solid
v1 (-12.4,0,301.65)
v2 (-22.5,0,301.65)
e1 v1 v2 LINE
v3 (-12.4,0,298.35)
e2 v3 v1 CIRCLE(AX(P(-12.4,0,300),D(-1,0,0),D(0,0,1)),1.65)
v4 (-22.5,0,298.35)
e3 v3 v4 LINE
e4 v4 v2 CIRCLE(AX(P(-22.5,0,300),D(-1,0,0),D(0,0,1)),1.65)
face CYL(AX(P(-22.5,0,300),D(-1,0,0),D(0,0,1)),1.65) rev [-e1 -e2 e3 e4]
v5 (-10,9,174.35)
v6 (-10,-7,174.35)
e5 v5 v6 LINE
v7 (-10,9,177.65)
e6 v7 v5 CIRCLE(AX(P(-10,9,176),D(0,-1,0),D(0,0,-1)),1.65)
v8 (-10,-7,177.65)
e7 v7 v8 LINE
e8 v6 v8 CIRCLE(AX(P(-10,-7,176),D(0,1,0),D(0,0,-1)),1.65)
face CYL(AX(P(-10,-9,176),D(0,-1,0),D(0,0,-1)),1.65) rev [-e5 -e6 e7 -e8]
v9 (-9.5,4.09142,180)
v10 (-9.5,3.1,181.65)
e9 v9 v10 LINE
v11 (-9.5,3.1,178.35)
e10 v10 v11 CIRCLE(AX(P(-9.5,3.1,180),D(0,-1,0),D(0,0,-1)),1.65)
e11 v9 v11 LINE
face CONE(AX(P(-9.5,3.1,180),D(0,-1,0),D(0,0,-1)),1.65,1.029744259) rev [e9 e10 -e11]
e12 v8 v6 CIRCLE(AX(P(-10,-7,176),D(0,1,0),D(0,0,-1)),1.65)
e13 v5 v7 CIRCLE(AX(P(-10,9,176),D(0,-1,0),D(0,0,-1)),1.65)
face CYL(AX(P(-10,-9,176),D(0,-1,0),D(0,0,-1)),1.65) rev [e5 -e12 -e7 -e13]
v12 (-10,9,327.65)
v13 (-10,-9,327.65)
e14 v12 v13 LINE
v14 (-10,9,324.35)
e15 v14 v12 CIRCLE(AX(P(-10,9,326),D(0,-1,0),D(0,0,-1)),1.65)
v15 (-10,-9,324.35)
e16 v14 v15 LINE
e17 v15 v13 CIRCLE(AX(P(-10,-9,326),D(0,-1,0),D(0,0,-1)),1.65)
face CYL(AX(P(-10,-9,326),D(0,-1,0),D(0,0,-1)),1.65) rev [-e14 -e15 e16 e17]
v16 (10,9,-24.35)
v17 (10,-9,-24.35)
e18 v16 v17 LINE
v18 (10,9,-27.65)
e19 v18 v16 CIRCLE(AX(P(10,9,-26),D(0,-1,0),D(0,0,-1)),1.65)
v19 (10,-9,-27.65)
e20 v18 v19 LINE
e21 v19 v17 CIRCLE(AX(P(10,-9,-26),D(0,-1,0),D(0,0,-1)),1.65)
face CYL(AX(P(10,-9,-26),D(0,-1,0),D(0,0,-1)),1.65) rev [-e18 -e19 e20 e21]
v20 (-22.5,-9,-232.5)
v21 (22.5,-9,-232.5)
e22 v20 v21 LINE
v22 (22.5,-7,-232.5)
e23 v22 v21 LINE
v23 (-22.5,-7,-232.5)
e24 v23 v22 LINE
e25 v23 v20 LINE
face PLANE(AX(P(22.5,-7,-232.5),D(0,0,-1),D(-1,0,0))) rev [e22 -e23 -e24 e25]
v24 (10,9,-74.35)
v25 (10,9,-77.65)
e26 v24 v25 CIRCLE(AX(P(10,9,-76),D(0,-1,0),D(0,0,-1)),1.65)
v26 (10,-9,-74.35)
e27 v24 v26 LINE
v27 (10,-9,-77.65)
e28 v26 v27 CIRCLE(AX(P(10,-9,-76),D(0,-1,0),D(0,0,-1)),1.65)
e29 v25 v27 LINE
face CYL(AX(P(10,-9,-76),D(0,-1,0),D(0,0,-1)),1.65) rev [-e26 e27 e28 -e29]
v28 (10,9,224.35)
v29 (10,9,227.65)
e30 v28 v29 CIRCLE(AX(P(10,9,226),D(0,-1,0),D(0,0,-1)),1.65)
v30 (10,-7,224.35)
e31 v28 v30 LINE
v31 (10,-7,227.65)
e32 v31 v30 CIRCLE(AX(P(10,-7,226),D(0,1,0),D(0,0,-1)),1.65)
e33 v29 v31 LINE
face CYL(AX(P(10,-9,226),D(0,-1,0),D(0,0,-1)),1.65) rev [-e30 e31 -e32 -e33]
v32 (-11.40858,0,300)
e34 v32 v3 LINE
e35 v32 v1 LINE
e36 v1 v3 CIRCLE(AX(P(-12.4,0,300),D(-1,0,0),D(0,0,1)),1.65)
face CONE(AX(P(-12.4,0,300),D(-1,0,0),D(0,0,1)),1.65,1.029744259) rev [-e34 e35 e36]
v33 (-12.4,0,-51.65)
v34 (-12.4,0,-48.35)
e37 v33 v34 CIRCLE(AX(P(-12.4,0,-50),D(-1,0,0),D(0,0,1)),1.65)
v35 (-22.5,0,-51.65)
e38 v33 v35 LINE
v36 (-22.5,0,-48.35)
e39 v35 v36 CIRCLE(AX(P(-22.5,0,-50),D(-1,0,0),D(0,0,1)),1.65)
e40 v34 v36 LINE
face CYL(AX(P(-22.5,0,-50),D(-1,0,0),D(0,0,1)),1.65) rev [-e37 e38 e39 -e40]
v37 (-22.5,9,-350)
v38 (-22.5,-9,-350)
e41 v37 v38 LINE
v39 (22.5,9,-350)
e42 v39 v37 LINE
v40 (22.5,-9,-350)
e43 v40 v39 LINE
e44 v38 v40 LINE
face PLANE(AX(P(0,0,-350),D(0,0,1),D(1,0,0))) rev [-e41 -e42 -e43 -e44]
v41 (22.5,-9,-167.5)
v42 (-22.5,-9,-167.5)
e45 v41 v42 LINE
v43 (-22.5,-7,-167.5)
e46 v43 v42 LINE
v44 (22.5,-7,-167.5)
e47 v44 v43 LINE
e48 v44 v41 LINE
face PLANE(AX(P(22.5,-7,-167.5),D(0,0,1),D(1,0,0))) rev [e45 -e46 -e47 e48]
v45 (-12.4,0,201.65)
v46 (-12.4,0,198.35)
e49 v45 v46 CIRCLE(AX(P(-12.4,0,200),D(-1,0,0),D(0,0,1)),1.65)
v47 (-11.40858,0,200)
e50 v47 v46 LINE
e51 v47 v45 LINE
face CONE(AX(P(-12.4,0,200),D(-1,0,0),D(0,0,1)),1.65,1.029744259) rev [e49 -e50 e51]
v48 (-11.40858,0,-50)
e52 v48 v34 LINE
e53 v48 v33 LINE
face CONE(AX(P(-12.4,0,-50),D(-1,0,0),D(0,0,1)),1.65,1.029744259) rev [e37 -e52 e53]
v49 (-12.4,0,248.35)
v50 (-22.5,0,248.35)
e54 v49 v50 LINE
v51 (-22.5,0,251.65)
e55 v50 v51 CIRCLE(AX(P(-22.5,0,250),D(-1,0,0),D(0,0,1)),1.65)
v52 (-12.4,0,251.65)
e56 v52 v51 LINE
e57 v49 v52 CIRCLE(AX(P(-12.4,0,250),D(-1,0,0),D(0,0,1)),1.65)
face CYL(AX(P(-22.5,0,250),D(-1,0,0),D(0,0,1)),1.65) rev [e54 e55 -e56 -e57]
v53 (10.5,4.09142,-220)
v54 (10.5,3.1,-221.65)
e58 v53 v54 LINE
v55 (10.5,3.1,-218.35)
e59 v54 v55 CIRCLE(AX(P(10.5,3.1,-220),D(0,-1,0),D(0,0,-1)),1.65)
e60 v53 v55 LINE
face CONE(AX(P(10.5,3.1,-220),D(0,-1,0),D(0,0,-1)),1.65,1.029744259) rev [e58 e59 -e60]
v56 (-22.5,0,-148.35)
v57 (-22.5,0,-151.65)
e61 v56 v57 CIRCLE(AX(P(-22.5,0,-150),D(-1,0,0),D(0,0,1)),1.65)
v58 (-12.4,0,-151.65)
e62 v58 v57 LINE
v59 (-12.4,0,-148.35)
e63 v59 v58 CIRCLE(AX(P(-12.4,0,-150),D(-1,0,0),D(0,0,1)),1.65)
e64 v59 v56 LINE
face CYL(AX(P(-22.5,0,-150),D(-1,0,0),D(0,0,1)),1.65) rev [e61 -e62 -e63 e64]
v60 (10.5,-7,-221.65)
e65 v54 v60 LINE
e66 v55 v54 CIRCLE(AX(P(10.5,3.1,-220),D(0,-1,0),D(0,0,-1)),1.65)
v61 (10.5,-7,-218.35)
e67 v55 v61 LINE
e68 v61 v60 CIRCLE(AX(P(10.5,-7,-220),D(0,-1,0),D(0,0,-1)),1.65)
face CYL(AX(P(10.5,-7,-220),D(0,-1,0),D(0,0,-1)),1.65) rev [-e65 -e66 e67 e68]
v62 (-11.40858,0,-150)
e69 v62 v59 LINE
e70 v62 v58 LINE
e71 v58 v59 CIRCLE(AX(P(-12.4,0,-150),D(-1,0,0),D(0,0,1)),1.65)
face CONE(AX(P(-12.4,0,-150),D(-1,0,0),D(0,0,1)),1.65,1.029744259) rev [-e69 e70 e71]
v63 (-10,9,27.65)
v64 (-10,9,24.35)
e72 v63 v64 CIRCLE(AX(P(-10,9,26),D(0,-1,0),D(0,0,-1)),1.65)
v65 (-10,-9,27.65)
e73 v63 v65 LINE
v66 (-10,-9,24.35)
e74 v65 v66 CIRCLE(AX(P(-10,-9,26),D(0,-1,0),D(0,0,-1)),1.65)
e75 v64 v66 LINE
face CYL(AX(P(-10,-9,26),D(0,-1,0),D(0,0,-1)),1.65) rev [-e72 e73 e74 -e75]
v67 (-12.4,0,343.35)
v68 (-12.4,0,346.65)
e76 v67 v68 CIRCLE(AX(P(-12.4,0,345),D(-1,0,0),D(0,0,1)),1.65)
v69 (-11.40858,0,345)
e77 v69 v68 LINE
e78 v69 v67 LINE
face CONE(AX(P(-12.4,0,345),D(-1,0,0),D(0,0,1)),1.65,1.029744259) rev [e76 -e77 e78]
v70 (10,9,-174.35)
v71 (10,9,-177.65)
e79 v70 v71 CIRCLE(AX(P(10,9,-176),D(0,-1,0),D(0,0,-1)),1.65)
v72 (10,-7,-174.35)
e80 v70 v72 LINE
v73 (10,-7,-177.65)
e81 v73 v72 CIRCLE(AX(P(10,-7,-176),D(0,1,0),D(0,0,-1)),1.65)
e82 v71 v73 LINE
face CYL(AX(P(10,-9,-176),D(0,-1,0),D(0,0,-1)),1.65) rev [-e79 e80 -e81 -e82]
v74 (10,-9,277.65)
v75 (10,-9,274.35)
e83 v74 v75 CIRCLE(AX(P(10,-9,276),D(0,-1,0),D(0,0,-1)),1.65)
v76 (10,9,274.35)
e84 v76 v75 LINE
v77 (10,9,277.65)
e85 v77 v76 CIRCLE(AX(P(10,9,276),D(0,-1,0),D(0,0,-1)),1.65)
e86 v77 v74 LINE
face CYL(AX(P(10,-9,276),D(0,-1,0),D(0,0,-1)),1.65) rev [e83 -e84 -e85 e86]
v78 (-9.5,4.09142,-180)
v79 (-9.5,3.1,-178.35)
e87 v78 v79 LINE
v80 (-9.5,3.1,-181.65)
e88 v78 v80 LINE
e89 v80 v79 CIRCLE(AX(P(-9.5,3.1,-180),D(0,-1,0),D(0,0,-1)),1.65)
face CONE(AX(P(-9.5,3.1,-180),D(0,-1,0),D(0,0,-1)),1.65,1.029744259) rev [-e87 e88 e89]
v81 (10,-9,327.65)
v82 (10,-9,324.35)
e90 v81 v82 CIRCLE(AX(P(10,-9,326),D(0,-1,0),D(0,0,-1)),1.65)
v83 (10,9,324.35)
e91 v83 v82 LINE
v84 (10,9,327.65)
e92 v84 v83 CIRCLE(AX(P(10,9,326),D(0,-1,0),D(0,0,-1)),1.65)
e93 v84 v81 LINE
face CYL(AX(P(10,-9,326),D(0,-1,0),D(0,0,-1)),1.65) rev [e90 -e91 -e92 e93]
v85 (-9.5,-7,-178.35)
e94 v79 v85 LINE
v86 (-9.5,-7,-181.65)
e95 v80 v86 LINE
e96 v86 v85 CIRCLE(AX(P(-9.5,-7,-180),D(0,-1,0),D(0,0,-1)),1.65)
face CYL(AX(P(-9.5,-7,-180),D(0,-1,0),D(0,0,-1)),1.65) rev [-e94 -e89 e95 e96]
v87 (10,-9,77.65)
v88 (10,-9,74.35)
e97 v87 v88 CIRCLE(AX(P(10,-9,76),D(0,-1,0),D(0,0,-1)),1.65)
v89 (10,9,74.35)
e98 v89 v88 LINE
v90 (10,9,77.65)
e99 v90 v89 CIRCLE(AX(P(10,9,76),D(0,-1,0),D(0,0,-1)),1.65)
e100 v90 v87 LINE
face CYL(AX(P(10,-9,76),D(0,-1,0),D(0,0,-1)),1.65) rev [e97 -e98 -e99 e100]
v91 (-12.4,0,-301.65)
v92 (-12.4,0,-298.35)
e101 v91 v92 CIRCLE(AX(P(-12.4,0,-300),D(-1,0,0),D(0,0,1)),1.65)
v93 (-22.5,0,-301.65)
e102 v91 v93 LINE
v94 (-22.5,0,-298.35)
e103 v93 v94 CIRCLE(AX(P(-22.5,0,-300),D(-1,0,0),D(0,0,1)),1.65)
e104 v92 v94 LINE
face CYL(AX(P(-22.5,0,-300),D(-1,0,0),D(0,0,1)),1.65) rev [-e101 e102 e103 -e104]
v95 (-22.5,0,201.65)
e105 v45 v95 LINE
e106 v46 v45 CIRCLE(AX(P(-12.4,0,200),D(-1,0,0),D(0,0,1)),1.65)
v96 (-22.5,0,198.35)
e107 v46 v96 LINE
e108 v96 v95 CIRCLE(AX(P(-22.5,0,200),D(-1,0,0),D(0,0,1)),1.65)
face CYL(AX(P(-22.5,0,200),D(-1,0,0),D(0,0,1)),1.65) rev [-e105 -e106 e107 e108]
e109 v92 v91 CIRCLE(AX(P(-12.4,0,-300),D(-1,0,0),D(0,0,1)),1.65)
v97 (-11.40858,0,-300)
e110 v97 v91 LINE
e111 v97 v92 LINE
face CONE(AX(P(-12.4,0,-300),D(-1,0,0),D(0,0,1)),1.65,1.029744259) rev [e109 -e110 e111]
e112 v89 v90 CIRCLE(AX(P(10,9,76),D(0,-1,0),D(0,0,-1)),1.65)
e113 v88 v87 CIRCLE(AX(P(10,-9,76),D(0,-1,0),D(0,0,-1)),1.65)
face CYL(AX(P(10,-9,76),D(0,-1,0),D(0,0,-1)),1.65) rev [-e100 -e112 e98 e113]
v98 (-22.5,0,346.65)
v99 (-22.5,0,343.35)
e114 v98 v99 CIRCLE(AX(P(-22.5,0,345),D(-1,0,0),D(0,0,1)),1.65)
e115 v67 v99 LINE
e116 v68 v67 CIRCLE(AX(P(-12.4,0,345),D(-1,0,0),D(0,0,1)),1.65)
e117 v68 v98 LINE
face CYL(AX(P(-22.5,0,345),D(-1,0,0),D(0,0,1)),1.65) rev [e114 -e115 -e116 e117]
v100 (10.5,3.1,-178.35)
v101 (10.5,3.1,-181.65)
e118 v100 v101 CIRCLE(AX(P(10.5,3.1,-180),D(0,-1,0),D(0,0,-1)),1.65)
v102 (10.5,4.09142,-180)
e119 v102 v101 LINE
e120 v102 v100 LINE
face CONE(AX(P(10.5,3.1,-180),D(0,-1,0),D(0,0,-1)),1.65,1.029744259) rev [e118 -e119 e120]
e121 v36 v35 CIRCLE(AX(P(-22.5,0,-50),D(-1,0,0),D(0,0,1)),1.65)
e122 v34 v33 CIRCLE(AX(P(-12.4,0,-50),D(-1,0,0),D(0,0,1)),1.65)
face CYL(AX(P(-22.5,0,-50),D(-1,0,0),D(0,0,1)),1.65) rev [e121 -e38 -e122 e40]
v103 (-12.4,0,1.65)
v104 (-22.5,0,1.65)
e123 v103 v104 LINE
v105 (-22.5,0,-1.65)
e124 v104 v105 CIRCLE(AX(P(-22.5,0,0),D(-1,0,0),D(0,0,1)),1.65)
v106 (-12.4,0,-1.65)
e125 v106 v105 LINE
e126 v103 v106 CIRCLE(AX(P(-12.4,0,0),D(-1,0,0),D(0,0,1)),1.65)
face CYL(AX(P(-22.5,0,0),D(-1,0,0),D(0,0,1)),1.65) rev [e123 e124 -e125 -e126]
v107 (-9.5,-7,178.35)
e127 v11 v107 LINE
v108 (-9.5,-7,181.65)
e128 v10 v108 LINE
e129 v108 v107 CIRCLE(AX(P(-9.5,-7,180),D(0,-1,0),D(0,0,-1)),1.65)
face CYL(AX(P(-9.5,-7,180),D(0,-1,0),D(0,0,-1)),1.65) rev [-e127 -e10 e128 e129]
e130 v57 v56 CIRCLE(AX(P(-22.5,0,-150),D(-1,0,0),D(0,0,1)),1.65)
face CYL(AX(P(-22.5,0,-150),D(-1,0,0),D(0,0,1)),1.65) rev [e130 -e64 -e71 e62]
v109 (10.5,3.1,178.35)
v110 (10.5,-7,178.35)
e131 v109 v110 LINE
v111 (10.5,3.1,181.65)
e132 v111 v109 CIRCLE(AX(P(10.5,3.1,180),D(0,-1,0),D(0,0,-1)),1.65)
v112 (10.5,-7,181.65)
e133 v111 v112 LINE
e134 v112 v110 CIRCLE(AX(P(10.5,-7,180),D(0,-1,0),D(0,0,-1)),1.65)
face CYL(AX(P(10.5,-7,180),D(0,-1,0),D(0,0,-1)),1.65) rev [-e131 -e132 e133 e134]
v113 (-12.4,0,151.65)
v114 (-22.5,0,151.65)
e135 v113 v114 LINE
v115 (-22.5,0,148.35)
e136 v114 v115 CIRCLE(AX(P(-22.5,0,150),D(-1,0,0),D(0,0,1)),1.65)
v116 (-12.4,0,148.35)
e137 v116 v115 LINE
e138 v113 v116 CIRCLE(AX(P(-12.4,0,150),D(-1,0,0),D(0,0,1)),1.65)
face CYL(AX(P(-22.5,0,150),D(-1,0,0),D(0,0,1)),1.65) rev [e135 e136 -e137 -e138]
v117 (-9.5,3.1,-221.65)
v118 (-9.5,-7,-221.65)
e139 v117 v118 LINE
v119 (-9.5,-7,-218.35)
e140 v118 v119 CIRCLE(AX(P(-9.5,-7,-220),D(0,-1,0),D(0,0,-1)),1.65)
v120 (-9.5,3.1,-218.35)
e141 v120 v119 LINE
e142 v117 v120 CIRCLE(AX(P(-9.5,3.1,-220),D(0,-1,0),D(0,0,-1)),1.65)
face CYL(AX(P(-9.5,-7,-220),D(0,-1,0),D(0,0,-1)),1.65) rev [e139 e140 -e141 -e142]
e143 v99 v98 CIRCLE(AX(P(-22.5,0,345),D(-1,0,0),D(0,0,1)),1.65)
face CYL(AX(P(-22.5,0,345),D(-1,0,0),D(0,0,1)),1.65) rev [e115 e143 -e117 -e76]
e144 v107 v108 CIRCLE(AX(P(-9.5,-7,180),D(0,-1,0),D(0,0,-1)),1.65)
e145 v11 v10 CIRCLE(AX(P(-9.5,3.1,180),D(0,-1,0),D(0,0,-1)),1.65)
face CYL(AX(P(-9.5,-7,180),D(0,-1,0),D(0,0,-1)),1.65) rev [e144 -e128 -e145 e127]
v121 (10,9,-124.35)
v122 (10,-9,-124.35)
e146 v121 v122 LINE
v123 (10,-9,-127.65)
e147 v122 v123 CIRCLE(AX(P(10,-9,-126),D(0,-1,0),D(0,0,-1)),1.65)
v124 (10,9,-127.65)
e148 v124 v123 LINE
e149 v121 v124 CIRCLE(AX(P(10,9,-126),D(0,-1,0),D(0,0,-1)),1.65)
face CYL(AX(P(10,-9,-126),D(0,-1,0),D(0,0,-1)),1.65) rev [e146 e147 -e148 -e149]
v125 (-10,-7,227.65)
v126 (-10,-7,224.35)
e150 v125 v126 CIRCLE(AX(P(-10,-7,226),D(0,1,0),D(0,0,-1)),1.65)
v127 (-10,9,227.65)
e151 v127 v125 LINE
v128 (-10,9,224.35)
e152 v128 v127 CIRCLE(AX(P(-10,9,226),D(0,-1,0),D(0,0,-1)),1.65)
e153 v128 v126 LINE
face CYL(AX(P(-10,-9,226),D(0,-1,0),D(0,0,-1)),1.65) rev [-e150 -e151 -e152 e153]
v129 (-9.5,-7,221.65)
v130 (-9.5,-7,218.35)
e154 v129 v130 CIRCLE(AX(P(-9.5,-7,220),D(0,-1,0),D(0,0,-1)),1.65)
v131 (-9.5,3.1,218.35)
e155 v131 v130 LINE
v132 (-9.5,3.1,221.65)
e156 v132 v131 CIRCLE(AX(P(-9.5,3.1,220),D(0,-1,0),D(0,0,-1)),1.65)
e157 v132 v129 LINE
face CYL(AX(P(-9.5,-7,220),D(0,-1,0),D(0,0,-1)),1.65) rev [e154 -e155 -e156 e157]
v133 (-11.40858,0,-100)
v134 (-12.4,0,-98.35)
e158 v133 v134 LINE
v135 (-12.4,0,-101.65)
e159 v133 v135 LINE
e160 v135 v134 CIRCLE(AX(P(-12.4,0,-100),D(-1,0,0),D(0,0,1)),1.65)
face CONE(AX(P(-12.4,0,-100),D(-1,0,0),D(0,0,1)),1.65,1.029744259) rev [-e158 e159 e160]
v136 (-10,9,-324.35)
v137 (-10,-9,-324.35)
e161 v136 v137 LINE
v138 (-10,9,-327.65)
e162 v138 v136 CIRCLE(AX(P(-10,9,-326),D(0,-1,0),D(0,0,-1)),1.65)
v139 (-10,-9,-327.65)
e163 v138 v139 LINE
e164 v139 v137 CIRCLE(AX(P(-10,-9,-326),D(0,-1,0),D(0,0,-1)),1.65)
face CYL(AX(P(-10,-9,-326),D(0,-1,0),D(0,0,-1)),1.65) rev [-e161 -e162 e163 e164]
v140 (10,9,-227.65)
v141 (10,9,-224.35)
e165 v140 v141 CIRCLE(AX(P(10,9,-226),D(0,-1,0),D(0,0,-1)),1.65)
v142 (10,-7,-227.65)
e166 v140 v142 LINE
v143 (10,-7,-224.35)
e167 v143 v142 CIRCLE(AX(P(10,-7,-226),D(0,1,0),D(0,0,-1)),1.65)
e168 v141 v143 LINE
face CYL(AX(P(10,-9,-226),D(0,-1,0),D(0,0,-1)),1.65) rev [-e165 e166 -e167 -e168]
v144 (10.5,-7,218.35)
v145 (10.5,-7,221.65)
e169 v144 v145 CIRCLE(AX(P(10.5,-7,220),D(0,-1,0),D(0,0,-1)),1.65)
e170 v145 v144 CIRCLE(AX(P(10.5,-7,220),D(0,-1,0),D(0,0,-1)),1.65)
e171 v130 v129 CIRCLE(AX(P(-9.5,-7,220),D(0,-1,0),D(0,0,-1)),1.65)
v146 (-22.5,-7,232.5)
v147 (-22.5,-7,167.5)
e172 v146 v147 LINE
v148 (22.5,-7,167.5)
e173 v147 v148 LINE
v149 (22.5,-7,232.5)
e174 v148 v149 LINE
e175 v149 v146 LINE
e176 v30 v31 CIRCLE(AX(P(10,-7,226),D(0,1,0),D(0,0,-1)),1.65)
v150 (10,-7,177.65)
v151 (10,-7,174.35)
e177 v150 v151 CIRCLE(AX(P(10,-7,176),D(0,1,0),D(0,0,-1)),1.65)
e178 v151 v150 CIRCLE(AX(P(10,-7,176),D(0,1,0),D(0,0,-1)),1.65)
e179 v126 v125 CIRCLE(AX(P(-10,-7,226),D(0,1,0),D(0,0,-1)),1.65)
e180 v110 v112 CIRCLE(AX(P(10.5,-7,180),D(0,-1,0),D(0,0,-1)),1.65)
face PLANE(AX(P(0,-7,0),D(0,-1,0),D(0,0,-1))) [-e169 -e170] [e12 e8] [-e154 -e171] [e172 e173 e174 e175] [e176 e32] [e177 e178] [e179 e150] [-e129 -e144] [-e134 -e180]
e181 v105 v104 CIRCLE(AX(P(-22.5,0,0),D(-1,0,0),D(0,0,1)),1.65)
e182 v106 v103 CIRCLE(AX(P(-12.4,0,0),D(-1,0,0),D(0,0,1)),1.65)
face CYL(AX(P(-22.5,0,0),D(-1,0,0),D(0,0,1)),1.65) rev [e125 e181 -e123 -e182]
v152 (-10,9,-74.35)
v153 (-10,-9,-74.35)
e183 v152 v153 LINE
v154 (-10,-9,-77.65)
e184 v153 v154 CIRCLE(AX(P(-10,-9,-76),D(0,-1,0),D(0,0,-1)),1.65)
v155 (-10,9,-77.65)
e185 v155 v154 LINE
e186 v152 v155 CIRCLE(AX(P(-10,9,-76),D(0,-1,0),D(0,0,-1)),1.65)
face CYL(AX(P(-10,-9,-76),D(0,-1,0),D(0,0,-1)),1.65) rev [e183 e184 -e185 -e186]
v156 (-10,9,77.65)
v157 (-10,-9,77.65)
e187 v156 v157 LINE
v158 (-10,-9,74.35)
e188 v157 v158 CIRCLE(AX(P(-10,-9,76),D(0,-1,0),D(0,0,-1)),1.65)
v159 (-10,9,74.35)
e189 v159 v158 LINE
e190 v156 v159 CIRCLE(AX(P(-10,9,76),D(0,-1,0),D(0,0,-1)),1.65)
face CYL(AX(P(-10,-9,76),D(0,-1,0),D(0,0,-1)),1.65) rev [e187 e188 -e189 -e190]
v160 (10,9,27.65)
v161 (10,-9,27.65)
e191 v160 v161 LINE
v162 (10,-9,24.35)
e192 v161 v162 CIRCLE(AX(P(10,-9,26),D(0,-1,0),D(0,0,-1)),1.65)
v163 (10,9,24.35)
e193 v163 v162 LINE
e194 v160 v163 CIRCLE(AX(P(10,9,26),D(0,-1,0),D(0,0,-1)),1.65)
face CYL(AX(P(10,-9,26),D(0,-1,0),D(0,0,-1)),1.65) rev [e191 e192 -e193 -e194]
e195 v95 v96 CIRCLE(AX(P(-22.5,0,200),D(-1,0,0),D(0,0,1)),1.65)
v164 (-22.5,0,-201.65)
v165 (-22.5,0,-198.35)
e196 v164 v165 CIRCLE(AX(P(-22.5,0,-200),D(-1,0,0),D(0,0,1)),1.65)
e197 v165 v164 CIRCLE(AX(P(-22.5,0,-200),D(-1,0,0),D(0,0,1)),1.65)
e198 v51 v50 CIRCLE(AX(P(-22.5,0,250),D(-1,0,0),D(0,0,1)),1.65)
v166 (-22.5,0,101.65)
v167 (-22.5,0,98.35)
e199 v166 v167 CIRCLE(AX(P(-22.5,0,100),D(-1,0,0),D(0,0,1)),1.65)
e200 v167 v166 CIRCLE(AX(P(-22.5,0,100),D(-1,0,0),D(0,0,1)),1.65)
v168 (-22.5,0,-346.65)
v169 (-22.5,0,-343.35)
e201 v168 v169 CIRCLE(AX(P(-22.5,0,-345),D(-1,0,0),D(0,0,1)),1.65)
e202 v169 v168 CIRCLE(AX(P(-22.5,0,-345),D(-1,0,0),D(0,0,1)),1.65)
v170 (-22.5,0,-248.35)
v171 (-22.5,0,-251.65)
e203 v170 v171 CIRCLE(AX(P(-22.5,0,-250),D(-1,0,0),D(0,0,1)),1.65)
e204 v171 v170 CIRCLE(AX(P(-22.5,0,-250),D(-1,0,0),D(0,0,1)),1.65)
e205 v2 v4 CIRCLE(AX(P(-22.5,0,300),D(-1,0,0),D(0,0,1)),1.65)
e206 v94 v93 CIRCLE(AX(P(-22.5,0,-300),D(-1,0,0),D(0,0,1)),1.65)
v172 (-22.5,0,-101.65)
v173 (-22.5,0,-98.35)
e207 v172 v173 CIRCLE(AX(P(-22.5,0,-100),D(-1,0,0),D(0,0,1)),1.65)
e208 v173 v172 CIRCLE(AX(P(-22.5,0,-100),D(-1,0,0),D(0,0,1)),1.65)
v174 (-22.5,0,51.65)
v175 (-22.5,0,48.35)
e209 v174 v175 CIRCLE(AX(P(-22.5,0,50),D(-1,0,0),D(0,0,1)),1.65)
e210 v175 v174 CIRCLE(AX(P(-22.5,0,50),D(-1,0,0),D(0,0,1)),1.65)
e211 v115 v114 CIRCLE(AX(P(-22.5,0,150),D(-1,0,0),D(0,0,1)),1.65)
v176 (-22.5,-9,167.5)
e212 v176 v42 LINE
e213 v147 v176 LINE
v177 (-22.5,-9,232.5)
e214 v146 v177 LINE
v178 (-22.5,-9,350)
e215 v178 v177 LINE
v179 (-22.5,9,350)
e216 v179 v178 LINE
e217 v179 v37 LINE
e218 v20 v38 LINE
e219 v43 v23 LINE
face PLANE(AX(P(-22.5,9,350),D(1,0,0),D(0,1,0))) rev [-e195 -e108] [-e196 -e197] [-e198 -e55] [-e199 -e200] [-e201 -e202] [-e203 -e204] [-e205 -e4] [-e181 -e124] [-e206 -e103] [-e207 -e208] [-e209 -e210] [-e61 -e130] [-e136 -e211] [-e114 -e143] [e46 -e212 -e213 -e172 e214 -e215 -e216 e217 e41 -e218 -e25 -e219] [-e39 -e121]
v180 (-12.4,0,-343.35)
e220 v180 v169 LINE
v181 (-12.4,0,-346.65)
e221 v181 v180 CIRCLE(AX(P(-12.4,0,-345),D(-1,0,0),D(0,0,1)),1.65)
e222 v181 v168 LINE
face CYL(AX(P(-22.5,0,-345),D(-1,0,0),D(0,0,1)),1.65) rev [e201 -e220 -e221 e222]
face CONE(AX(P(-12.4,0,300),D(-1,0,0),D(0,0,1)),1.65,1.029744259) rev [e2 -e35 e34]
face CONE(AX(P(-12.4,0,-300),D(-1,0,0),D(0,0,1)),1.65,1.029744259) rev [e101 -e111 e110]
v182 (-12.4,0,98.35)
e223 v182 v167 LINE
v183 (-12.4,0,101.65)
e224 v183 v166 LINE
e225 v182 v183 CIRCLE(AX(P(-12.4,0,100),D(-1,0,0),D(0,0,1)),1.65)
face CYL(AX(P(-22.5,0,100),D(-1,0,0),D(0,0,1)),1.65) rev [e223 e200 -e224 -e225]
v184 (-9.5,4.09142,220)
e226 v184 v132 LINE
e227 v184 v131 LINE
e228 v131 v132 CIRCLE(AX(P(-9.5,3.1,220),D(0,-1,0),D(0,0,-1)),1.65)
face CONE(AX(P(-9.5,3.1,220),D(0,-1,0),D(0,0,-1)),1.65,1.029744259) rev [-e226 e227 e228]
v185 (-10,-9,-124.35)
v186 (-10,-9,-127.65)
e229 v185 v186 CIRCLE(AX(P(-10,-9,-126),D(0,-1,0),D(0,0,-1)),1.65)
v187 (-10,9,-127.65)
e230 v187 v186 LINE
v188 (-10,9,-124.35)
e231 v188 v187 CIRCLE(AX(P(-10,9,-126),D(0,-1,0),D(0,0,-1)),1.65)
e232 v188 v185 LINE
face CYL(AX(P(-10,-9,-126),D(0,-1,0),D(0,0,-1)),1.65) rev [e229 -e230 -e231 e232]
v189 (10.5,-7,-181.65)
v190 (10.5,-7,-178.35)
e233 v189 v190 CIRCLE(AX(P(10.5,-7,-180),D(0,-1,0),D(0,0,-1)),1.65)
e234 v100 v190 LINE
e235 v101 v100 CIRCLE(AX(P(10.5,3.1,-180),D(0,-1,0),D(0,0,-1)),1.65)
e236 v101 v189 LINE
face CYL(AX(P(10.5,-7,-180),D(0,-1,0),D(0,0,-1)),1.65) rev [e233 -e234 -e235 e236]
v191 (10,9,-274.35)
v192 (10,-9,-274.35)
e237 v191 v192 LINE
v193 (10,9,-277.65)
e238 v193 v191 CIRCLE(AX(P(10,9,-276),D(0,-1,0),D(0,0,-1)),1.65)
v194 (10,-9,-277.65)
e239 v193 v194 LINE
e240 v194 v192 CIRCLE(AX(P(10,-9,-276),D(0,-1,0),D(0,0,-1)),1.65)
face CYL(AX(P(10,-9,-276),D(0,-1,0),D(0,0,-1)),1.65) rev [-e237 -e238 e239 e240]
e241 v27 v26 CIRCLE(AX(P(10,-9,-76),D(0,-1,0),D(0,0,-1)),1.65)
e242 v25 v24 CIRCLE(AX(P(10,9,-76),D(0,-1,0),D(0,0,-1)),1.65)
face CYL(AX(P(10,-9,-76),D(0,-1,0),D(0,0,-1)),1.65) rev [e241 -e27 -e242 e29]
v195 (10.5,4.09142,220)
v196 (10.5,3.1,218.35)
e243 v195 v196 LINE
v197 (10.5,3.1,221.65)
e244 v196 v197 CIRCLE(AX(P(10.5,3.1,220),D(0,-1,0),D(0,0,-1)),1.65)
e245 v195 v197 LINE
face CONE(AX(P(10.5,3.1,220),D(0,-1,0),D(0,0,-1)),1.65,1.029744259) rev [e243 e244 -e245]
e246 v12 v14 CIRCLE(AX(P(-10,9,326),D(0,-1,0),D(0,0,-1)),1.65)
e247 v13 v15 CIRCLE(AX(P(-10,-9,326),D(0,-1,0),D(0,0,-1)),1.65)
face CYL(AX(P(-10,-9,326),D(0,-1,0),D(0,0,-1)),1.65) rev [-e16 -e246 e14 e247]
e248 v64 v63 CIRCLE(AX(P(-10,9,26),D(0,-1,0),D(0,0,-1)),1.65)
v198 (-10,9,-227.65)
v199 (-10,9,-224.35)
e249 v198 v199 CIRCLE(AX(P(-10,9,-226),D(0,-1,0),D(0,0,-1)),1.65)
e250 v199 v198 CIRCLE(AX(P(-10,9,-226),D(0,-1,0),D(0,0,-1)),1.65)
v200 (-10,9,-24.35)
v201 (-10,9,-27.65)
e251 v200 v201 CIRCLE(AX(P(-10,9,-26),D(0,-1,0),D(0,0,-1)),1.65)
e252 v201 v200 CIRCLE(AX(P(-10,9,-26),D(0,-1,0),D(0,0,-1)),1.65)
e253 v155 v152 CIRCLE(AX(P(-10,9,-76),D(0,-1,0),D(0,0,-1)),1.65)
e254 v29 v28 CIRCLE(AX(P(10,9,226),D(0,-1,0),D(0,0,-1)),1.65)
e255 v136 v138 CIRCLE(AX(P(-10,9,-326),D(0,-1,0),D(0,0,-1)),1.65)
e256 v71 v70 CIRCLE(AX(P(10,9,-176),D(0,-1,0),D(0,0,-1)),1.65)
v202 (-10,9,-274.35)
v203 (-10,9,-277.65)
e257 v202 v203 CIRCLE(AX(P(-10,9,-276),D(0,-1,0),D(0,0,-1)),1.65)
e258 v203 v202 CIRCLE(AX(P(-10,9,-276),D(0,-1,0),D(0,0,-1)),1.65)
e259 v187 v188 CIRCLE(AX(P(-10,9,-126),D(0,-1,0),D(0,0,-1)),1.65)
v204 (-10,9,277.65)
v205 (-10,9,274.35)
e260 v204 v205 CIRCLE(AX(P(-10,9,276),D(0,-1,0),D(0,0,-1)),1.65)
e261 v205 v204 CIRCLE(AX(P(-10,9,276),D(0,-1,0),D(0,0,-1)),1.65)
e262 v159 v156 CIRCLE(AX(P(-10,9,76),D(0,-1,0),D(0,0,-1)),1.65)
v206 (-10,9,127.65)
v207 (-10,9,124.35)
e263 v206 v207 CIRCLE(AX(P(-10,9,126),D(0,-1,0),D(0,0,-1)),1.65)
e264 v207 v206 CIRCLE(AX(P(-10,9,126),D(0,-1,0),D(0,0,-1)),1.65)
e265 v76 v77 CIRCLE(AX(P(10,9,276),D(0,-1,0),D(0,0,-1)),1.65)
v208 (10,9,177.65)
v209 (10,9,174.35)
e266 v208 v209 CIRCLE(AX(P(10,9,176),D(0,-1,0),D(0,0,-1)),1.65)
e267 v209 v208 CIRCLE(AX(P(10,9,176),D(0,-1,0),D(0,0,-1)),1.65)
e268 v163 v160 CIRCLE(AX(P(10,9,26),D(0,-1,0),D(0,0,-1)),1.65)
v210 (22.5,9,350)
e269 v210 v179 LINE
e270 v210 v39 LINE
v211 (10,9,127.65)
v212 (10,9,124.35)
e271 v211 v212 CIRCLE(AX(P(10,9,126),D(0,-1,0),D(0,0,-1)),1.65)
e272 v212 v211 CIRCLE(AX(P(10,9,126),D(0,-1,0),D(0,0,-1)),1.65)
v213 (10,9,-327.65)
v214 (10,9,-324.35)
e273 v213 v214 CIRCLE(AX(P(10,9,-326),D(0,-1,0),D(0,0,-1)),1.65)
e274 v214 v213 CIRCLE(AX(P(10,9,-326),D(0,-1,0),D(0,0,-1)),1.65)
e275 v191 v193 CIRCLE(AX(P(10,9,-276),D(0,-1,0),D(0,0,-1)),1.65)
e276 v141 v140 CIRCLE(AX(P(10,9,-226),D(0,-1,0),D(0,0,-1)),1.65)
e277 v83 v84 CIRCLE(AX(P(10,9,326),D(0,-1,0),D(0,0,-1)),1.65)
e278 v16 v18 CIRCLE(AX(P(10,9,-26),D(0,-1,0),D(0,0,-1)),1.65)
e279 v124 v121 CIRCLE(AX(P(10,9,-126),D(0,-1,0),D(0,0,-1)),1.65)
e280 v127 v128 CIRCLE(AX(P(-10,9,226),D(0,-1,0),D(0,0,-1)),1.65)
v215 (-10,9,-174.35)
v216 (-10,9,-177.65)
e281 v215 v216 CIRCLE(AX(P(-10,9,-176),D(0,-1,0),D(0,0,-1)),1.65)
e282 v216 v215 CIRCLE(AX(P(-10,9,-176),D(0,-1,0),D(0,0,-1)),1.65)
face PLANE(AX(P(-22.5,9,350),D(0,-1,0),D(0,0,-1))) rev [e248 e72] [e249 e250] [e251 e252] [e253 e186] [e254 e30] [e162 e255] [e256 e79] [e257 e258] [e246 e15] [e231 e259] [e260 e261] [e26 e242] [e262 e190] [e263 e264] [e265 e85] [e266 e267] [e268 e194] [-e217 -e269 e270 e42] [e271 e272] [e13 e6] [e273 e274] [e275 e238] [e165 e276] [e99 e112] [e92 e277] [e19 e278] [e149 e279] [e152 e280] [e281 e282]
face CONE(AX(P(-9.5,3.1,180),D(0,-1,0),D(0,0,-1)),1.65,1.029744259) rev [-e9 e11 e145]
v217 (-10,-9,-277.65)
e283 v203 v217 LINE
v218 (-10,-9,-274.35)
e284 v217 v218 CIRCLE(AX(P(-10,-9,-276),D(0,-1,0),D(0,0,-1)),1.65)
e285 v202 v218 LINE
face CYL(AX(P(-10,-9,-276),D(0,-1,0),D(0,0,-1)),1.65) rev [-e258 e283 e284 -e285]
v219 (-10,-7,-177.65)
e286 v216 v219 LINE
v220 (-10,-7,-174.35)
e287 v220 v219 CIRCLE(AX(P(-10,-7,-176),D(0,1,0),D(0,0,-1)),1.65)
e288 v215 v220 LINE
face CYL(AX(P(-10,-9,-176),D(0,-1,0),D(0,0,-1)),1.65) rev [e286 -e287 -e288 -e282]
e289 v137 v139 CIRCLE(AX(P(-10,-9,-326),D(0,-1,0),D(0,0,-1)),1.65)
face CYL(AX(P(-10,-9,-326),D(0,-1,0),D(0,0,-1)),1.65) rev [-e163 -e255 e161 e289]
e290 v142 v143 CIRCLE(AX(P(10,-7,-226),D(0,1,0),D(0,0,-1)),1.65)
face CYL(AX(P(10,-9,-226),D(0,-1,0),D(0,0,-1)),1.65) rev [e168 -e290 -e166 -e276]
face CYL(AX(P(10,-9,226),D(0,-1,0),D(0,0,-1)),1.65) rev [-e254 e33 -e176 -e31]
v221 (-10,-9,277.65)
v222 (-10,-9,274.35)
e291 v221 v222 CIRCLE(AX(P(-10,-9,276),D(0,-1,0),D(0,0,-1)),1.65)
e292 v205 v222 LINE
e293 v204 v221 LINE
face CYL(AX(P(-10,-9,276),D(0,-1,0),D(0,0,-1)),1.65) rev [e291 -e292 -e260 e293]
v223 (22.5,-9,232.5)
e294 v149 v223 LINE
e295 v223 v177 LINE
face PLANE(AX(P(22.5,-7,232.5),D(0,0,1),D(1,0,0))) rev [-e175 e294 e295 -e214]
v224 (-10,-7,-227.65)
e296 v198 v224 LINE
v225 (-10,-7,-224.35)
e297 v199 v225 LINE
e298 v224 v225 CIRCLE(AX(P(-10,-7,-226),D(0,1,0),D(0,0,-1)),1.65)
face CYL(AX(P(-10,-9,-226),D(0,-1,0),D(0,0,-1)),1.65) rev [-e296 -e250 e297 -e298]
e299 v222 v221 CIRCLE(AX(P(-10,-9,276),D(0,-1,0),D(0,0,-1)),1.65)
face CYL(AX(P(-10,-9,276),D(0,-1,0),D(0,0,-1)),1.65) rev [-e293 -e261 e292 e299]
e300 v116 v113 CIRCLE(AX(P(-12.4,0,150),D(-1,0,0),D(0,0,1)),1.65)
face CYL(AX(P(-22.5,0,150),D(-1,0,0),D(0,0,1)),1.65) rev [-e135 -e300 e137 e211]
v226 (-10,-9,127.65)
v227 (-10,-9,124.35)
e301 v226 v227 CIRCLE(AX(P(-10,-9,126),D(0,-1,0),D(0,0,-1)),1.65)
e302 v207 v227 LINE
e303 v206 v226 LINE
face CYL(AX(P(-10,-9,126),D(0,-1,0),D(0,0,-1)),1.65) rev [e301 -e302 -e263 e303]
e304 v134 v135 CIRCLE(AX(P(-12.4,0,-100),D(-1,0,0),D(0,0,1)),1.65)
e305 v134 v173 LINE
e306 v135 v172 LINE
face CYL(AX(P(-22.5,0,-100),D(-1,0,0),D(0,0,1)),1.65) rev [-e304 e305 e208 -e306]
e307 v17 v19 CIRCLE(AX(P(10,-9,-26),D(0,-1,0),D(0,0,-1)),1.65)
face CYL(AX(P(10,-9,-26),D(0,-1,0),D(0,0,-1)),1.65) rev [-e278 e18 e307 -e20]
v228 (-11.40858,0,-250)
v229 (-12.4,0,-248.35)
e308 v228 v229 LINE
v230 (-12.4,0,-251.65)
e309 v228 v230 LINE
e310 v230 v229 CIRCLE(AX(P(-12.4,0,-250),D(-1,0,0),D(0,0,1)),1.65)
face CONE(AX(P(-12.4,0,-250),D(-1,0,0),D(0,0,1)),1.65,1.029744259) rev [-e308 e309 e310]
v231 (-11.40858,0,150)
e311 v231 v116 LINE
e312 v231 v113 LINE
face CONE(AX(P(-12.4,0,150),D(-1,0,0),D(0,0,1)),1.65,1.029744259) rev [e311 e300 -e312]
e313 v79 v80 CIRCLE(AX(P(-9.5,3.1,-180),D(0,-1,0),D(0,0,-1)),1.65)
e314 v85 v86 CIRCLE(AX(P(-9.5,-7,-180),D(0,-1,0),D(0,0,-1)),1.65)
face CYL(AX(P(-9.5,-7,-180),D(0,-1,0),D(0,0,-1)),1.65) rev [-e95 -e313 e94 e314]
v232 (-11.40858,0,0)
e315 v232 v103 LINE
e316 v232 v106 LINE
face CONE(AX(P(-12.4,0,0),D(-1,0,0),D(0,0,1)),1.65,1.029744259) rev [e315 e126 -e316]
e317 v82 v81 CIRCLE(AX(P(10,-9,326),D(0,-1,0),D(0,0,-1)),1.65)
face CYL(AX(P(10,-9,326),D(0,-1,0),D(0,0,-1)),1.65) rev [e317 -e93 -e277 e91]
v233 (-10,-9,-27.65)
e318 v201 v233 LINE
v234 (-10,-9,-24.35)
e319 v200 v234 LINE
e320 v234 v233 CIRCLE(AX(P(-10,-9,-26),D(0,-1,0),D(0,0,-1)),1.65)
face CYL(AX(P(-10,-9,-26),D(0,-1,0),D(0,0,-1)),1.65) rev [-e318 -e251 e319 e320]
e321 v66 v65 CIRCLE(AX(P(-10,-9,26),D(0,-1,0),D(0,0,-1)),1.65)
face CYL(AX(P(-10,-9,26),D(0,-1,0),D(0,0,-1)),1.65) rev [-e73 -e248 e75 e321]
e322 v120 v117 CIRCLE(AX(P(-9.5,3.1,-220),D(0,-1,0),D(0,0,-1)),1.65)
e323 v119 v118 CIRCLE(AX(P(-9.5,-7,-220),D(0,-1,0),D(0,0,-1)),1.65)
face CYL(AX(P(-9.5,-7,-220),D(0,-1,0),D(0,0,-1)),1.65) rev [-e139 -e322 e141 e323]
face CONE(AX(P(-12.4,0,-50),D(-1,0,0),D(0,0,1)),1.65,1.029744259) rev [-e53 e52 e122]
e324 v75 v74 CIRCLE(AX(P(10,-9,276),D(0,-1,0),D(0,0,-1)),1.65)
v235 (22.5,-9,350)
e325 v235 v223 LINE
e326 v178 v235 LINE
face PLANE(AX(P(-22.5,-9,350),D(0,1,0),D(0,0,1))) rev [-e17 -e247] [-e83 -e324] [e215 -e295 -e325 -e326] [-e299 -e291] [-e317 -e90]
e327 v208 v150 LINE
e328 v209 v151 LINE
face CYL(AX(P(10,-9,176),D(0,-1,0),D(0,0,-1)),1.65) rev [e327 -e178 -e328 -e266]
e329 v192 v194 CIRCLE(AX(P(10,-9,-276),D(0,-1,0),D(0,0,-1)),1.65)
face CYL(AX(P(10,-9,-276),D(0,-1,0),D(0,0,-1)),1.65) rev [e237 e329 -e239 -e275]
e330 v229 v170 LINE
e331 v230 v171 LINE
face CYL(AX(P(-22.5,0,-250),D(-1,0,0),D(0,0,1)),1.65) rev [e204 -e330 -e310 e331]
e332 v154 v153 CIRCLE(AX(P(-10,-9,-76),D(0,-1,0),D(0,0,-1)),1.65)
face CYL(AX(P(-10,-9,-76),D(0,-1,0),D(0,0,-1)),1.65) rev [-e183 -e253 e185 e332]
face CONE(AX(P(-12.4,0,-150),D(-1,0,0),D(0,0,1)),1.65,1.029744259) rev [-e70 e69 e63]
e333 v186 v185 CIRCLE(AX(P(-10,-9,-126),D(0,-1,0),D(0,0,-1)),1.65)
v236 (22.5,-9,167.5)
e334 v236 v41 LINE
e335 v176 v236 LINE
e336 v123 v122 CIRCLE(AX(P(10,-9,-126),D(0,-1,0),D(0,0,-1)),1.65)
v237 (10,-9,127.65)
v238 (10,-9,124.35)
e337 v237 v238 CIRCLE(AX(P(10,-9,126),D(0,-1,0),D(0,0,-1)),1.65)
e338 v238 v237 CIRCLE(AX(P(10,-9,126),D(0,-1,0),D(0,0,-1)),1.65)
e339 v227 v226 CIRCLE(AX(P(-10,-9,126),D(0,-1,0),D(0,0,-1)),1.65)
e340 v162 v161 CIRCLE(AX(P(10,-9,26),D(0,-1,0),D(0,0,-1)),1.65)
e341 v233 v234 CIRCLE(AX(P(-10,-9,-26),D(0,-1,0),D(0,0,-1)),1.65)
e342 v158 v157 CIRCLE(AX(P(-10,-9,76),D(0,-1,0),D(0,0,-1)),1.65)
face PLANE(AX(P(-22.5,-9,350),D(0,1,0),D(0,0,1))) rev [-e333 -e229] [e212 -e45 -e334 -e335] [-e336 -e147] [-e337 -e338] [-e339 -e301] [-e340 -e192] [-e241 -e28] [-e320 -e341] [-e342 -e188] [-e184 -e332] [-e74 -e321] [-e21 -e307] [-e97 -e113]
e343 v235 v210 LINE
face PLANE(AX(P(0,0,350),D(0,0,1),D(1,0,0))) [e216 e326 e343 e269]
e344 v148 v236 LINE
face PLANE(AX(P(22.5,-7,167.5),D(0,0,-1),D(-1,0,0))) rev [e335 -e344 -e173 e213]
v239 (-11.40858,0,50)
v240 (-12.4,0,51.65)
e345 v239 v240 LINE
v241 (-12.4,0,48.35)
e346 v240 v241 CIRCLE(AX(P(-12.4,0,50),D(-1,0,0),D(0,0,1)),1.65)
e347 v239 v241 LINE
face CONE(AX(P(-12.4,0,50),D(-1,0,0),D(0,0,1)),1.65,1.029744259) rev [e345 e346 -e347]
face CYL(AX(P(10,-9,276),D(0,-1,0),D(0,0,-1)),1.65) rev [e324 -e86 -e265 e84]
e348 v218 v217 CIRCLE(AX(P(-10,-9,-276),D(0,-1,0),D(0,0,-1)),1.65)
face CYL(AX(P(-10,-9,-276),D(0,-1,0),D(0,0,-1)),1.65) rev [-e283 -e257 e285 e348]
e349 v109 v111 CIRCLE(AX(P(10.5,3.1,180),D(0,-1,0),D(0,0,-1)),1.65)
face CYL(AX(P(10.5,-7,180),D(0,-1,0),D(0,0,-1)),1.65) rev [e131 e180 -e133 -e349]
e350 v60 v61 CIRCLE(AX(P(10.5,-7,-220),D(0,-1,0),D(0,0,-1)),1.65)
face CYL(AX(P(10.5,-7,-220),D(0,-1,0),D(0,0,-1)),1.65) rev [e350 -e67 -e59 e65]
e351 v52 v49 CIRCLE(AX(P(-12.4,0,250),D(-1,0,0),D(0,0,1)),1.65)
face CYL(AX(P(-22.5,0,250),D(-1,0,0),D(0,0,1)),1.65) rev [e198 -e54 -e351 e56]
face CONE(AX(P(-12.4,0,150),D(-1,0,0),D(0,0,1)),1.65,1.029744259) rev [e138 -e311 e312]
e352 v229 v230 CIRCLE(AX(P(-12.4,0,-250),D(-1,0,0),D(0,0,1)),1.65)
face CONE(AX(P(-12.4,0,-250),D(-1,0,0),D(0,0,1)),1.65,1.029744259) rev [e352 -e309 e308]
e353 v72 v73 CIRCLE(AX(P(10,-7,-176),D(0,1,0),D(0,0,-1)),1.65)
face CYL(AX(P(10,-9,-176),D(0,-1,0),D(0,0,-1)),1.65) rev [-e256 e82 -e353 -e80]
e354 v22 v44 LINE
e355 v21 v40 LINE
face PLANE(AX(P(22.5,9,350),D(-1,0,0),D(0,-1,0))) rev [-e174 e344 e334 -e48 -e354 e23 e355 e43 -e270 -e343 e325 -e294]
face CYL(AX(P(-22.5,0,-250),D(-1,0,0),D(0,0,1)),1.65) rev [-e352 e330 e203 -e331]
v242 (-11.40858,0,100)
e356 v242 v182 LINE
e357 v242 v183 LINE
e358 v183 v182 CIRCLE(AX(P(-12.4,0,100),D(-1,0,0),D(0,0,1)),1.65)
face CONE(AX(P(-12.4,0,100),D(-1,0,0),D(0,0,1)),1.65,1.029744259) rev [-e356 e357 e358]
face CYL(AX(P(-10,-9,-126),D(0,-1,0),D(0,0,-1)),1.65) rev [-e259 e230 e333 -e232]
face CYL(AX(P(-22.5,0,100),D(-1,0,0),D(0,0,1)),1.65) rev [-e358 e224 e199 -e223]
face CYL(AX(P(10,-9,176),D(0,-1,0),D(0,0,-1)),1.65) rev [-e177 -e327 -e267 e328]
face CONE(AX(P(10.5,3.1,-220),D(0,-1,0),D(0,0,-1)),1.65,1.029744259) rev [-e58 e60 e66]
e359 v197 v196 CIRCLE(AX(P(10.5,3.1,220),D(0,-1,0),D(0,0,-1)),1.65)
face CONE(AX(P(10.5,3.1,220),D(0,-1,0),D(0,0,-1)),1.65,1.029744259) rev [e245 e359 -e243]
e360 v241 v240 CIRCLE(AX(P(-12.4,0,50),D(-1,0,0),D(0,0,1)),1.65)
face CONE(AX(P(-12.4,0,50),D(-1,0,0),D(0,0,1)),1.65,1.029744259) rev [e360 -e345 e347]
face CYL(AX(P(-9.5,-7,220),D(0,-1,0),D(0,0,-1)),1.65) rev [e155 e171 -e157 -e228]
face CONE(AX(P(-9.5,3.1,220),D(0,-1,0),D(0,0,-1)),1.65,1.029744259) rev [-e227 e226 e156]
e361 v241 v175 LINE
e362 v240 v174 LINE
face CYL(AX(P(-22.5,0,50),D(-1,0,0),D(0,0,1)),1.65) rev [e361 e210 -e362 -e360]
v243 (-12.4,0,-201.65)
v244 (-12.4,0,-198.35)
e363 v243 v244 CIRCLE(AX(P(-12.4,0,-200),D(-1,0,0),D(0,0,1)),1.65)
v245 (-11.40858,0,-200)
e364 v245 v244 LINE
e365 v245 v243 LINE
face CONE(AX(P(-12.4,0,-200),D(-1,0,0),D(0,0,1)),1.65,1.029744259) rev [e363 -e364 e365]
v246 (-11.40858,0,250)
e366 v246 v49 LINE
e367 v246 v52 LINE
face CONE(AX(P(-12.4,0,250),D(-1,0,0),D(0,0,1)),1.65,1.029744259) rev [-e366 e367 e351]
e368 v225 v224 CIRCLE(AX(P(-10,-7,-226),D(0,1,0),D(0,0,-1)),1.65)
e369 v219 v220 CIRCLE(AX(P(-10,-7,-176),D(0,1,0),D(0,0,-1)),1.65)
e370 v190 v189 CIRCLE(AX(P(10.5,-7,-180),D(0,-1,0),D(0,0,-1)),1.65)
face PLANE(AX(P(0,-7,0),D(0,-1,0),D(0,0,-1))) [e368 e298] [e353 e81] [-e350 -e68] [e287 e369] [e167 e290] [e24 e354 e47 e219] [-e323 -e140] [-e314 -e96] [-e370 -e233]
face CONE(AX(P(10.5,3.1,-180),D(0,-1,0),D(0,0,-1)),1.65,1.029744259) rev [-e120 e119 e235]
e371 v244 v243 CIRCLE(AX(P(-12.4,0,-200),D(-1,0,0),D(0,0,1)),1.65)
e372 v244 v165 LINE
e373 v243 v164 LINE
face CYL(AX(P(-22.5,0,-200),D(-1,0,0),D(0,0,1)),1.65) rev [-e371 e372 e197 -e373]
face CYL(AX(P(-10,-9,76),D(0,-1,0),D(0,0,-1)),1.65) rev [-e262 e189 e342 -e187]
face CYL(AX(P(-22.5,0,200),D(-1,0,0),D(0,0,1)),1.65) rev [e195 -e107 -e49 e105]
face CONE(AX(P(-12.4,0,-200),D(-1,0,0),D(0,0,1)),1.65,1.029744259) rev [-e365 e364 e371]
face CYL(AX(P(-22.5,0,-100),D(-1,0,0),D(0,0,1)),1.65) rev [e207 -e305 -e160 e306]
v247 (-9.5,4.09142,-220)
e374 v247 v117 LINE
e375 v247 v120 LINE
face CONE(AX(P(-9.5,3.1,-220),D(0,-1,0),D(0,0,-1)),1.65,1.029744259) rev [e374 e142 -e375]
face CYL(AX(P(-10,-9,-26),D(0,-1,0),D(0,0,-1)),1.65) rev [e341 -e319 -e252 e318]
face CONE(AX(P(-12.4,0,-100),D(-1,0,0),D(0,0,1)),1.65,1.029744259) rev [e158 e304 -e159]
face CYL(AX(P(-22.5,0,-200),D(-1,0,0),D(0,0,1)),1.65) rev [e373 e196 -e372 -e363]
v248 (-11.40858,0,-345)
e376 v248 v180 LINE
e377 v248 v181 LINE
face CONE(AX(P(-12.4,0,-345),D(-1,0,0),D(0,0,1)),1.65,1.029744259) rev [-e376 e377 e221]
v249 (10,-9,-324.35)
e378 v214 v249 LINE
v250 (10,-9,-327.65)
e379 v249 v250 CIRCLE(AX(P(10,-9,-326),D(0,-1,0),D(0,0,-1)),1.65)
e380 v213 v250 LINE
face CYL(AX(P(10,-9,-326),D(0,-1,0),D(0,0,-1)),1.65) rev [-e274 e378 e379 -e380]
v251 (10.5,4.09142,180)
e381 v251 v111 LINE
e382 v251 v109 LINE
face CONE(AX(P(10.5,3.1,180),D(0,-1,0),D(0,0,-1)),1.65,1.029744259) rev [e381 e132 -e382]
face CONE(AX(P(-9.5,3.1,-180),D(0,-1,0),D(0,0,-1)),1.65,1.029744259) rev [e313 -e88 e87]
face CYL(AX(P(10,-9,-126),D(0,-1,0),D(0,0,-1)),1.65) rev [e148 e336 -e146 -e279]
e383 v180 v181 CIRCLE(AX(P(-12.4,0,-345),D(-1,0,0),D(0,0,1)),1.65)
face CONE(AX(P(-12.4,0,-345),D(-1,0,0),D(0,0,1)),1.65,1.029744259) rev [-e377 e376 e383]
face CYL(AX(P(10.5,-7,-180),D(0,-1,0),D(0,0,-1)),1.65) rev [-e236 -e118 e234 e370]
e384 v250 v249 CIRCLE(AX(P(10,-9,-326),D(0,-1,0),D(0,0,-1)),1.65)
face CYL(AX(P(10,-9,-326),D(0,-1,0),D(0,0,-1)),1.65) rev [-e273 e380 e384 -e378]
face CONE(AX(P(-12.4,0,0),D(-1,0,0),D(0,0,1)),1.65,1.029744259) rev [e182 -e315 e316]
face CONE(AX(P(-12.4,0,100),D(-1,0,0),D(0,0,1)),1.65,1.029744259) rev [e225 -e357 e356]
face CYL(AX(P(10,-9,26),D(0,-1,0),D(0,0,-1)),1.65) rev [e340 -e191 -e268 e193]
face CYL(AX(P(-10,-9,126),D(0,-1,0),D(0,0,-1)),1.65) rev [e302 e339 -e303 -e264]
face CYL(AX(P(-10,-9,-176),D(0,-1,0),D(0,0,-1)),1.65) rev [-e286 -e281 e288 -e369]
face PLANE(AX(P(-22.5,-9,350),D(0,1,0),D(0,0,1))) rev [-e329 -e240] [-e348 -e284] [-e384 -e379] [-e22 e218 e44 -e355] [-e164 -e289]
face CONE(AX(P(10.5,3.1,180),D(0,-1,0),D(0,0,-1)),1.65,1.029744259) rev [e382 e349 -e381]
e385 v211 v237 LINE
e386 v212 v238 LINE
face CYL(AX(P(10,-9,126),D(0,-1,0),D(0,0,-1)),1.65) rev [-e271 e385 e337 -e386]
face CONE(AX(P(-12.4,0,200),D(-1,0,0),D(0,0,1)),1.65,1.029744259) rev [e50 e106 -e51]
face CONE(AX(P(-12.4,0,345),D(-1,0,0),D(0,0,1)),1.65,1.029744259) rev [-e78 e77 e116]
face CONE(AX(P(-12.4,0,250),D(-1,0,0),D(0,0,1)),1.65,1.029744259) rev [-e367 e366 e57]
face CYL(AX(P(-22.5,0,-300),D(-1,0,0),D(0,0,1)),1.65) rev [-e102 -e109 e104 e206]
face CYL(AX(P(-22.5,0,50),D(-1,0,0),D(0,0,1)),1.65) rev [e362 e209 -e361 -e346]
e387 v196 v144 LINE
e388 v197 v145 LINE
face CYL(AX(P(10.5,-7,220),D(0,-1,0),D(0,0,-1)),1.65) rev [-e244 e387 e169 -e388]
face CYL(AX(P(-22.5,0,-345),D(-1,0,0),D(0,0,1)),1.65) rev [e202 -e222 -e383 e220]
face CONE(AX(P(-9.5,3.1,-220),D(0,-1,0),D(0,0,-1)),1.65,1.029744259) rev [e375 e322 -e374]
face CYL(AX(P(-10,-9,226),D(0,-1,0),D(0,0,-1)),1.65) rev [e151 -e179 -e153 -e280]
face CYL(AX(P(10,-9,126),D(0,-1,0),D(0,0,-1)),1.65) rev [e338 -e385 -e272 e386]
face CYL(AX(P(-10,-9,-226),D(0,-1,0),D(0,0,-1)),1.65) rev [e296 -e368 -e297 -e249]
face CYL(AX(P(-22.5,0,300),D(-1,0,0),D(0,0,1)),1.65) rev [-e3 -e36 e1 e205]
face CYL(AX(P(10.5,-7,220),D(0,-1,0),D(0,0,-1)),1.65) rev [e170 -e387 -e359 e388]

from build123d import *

# Parameters (mm, degrees)
SKETCH1_W             = 45
SKETCH1_H             = 18
BOSS_EXTRUDE1_DEPTH   = 350
M4_TAPPED_HOLE1_D     = 3.3
M4_TAPPED_HOLE1_DEPTH = 10.1
M4_TAPPED_HOLE1_TIP   = 0.991420021
M4_TAPPED_HOLE3_D     = 3.3
SKETCH10_W            = 45
SKETCH10_H            = 65
CUT_EXTRUDE3_DEPTH    = 2
M4_TAPPED_HOLE2_D     = 3.3
M4_TAPPED_HOLE2_DEPTH = 10.1
M4_TAPPED_HOLE2_TIP   = 0.991420021


with BuildPart() as part:
    # Sketch1 → Boss-Extrude1 (new, symmetric)
    with BuildSketch(Plane.XY):
        Rectangle(SKETCH1_W, SKETCH1_H)
    extrude(amount=BOSS_EXTRUDE1_DEPTH, both=True)

    # M4 Tapped Hole1
    with Locations(Plane.ZY.offset(22.5)):
        with Locations((-345, 0), (-300, 0), (-250, 0), (-200, 0), (-150, 0), (-100, 0), (-50, 0), (0, 0), (50, 0), (100, 0), (150, 0), (200, 0), (250, 0), (300, 0), (345, 0)):
            Hole(M4_TAPPED_HOLE1_D / 2, depth=M4_TAPPED_HOLE1_DEPTH)
            with Locations((0, 0, -(M4_TAPPED_HOLE1_DEPTH + M4_TAPPED_HOLE1_TIP / 2))):  # 118° drill point
                Cone(0, M4_TAPPED_HOLE1_D / 2, M4_TAPPED_HOLE1_TIP, mode=Mode.SUBTRACT)

    # M4 Tapped Hole3 (through all)
    with Locations(Plane(origin=(0, -9, 0), x_dir=(-1, 0, 0), z_dir=(0, -1, 0))):
        with Locations((10, -176), (-10, -176), (10, -126), (-10, -126), (10, -226), (-10, -226), (10, -276), (-10, -76), (10, -76), (-10, -276), (10, -326), (-10, -326), (10, 176), (-10, 176), (10, 226), (-10, 226), (10, 326), (-10, 326), (-10, 276), (10, 276), (10, 126), (-10, 126), (-10, 76), (10, 76), (10, 26), (-10, 26), (10, -26), (-10, -26)):
            Hole(M4_TAPPED_HOLE3_D / 2)

    # Sketch10 → Cut-Extrude3 (cut)
    with BuildSketch(Plane.XZ.offset(9)):
        with Locations((0, 200)):
            Rectangle(SKETCH10_W, SKETCH10_H)
        with Locations((0, -200)):
            Rectangle(SKETCH10_W, SKETCH10_H)
    extrude(amount=-CUT_EXTRUDE3_DEPTH, mode=Mode.SUBTRACT)

    # M4 Tapped Hole2
    with Locations(Plane(origin=(0, -7, 0), x_dir=(-1, 0, 0), z_dir=(0, -1, 0))):
        with Locations((9.5, -220), (-10.5, -220), (-10.5, -180), (9.5, -180), (9.5, 180), (-10.5, 180), (-10.5, 220), (9.5, 220)):
            Hole(M4_TAPPED_HOLE2_D / 2, depth=M4_TAPPED_HOLE2_DEPTH)
            with Locations((0, 0, -(M4_TAPPED_HOLE2_DEPTH + M4_TAPPED_HOLE2_TIP / 2))):  # 118° drill point
                Cone(0, M4_TAPPED_HOLE2_D / 2, M4_TAPPED_HOLE2_TIP, mode=Mode.SUBTRACT)


solid = part.part
